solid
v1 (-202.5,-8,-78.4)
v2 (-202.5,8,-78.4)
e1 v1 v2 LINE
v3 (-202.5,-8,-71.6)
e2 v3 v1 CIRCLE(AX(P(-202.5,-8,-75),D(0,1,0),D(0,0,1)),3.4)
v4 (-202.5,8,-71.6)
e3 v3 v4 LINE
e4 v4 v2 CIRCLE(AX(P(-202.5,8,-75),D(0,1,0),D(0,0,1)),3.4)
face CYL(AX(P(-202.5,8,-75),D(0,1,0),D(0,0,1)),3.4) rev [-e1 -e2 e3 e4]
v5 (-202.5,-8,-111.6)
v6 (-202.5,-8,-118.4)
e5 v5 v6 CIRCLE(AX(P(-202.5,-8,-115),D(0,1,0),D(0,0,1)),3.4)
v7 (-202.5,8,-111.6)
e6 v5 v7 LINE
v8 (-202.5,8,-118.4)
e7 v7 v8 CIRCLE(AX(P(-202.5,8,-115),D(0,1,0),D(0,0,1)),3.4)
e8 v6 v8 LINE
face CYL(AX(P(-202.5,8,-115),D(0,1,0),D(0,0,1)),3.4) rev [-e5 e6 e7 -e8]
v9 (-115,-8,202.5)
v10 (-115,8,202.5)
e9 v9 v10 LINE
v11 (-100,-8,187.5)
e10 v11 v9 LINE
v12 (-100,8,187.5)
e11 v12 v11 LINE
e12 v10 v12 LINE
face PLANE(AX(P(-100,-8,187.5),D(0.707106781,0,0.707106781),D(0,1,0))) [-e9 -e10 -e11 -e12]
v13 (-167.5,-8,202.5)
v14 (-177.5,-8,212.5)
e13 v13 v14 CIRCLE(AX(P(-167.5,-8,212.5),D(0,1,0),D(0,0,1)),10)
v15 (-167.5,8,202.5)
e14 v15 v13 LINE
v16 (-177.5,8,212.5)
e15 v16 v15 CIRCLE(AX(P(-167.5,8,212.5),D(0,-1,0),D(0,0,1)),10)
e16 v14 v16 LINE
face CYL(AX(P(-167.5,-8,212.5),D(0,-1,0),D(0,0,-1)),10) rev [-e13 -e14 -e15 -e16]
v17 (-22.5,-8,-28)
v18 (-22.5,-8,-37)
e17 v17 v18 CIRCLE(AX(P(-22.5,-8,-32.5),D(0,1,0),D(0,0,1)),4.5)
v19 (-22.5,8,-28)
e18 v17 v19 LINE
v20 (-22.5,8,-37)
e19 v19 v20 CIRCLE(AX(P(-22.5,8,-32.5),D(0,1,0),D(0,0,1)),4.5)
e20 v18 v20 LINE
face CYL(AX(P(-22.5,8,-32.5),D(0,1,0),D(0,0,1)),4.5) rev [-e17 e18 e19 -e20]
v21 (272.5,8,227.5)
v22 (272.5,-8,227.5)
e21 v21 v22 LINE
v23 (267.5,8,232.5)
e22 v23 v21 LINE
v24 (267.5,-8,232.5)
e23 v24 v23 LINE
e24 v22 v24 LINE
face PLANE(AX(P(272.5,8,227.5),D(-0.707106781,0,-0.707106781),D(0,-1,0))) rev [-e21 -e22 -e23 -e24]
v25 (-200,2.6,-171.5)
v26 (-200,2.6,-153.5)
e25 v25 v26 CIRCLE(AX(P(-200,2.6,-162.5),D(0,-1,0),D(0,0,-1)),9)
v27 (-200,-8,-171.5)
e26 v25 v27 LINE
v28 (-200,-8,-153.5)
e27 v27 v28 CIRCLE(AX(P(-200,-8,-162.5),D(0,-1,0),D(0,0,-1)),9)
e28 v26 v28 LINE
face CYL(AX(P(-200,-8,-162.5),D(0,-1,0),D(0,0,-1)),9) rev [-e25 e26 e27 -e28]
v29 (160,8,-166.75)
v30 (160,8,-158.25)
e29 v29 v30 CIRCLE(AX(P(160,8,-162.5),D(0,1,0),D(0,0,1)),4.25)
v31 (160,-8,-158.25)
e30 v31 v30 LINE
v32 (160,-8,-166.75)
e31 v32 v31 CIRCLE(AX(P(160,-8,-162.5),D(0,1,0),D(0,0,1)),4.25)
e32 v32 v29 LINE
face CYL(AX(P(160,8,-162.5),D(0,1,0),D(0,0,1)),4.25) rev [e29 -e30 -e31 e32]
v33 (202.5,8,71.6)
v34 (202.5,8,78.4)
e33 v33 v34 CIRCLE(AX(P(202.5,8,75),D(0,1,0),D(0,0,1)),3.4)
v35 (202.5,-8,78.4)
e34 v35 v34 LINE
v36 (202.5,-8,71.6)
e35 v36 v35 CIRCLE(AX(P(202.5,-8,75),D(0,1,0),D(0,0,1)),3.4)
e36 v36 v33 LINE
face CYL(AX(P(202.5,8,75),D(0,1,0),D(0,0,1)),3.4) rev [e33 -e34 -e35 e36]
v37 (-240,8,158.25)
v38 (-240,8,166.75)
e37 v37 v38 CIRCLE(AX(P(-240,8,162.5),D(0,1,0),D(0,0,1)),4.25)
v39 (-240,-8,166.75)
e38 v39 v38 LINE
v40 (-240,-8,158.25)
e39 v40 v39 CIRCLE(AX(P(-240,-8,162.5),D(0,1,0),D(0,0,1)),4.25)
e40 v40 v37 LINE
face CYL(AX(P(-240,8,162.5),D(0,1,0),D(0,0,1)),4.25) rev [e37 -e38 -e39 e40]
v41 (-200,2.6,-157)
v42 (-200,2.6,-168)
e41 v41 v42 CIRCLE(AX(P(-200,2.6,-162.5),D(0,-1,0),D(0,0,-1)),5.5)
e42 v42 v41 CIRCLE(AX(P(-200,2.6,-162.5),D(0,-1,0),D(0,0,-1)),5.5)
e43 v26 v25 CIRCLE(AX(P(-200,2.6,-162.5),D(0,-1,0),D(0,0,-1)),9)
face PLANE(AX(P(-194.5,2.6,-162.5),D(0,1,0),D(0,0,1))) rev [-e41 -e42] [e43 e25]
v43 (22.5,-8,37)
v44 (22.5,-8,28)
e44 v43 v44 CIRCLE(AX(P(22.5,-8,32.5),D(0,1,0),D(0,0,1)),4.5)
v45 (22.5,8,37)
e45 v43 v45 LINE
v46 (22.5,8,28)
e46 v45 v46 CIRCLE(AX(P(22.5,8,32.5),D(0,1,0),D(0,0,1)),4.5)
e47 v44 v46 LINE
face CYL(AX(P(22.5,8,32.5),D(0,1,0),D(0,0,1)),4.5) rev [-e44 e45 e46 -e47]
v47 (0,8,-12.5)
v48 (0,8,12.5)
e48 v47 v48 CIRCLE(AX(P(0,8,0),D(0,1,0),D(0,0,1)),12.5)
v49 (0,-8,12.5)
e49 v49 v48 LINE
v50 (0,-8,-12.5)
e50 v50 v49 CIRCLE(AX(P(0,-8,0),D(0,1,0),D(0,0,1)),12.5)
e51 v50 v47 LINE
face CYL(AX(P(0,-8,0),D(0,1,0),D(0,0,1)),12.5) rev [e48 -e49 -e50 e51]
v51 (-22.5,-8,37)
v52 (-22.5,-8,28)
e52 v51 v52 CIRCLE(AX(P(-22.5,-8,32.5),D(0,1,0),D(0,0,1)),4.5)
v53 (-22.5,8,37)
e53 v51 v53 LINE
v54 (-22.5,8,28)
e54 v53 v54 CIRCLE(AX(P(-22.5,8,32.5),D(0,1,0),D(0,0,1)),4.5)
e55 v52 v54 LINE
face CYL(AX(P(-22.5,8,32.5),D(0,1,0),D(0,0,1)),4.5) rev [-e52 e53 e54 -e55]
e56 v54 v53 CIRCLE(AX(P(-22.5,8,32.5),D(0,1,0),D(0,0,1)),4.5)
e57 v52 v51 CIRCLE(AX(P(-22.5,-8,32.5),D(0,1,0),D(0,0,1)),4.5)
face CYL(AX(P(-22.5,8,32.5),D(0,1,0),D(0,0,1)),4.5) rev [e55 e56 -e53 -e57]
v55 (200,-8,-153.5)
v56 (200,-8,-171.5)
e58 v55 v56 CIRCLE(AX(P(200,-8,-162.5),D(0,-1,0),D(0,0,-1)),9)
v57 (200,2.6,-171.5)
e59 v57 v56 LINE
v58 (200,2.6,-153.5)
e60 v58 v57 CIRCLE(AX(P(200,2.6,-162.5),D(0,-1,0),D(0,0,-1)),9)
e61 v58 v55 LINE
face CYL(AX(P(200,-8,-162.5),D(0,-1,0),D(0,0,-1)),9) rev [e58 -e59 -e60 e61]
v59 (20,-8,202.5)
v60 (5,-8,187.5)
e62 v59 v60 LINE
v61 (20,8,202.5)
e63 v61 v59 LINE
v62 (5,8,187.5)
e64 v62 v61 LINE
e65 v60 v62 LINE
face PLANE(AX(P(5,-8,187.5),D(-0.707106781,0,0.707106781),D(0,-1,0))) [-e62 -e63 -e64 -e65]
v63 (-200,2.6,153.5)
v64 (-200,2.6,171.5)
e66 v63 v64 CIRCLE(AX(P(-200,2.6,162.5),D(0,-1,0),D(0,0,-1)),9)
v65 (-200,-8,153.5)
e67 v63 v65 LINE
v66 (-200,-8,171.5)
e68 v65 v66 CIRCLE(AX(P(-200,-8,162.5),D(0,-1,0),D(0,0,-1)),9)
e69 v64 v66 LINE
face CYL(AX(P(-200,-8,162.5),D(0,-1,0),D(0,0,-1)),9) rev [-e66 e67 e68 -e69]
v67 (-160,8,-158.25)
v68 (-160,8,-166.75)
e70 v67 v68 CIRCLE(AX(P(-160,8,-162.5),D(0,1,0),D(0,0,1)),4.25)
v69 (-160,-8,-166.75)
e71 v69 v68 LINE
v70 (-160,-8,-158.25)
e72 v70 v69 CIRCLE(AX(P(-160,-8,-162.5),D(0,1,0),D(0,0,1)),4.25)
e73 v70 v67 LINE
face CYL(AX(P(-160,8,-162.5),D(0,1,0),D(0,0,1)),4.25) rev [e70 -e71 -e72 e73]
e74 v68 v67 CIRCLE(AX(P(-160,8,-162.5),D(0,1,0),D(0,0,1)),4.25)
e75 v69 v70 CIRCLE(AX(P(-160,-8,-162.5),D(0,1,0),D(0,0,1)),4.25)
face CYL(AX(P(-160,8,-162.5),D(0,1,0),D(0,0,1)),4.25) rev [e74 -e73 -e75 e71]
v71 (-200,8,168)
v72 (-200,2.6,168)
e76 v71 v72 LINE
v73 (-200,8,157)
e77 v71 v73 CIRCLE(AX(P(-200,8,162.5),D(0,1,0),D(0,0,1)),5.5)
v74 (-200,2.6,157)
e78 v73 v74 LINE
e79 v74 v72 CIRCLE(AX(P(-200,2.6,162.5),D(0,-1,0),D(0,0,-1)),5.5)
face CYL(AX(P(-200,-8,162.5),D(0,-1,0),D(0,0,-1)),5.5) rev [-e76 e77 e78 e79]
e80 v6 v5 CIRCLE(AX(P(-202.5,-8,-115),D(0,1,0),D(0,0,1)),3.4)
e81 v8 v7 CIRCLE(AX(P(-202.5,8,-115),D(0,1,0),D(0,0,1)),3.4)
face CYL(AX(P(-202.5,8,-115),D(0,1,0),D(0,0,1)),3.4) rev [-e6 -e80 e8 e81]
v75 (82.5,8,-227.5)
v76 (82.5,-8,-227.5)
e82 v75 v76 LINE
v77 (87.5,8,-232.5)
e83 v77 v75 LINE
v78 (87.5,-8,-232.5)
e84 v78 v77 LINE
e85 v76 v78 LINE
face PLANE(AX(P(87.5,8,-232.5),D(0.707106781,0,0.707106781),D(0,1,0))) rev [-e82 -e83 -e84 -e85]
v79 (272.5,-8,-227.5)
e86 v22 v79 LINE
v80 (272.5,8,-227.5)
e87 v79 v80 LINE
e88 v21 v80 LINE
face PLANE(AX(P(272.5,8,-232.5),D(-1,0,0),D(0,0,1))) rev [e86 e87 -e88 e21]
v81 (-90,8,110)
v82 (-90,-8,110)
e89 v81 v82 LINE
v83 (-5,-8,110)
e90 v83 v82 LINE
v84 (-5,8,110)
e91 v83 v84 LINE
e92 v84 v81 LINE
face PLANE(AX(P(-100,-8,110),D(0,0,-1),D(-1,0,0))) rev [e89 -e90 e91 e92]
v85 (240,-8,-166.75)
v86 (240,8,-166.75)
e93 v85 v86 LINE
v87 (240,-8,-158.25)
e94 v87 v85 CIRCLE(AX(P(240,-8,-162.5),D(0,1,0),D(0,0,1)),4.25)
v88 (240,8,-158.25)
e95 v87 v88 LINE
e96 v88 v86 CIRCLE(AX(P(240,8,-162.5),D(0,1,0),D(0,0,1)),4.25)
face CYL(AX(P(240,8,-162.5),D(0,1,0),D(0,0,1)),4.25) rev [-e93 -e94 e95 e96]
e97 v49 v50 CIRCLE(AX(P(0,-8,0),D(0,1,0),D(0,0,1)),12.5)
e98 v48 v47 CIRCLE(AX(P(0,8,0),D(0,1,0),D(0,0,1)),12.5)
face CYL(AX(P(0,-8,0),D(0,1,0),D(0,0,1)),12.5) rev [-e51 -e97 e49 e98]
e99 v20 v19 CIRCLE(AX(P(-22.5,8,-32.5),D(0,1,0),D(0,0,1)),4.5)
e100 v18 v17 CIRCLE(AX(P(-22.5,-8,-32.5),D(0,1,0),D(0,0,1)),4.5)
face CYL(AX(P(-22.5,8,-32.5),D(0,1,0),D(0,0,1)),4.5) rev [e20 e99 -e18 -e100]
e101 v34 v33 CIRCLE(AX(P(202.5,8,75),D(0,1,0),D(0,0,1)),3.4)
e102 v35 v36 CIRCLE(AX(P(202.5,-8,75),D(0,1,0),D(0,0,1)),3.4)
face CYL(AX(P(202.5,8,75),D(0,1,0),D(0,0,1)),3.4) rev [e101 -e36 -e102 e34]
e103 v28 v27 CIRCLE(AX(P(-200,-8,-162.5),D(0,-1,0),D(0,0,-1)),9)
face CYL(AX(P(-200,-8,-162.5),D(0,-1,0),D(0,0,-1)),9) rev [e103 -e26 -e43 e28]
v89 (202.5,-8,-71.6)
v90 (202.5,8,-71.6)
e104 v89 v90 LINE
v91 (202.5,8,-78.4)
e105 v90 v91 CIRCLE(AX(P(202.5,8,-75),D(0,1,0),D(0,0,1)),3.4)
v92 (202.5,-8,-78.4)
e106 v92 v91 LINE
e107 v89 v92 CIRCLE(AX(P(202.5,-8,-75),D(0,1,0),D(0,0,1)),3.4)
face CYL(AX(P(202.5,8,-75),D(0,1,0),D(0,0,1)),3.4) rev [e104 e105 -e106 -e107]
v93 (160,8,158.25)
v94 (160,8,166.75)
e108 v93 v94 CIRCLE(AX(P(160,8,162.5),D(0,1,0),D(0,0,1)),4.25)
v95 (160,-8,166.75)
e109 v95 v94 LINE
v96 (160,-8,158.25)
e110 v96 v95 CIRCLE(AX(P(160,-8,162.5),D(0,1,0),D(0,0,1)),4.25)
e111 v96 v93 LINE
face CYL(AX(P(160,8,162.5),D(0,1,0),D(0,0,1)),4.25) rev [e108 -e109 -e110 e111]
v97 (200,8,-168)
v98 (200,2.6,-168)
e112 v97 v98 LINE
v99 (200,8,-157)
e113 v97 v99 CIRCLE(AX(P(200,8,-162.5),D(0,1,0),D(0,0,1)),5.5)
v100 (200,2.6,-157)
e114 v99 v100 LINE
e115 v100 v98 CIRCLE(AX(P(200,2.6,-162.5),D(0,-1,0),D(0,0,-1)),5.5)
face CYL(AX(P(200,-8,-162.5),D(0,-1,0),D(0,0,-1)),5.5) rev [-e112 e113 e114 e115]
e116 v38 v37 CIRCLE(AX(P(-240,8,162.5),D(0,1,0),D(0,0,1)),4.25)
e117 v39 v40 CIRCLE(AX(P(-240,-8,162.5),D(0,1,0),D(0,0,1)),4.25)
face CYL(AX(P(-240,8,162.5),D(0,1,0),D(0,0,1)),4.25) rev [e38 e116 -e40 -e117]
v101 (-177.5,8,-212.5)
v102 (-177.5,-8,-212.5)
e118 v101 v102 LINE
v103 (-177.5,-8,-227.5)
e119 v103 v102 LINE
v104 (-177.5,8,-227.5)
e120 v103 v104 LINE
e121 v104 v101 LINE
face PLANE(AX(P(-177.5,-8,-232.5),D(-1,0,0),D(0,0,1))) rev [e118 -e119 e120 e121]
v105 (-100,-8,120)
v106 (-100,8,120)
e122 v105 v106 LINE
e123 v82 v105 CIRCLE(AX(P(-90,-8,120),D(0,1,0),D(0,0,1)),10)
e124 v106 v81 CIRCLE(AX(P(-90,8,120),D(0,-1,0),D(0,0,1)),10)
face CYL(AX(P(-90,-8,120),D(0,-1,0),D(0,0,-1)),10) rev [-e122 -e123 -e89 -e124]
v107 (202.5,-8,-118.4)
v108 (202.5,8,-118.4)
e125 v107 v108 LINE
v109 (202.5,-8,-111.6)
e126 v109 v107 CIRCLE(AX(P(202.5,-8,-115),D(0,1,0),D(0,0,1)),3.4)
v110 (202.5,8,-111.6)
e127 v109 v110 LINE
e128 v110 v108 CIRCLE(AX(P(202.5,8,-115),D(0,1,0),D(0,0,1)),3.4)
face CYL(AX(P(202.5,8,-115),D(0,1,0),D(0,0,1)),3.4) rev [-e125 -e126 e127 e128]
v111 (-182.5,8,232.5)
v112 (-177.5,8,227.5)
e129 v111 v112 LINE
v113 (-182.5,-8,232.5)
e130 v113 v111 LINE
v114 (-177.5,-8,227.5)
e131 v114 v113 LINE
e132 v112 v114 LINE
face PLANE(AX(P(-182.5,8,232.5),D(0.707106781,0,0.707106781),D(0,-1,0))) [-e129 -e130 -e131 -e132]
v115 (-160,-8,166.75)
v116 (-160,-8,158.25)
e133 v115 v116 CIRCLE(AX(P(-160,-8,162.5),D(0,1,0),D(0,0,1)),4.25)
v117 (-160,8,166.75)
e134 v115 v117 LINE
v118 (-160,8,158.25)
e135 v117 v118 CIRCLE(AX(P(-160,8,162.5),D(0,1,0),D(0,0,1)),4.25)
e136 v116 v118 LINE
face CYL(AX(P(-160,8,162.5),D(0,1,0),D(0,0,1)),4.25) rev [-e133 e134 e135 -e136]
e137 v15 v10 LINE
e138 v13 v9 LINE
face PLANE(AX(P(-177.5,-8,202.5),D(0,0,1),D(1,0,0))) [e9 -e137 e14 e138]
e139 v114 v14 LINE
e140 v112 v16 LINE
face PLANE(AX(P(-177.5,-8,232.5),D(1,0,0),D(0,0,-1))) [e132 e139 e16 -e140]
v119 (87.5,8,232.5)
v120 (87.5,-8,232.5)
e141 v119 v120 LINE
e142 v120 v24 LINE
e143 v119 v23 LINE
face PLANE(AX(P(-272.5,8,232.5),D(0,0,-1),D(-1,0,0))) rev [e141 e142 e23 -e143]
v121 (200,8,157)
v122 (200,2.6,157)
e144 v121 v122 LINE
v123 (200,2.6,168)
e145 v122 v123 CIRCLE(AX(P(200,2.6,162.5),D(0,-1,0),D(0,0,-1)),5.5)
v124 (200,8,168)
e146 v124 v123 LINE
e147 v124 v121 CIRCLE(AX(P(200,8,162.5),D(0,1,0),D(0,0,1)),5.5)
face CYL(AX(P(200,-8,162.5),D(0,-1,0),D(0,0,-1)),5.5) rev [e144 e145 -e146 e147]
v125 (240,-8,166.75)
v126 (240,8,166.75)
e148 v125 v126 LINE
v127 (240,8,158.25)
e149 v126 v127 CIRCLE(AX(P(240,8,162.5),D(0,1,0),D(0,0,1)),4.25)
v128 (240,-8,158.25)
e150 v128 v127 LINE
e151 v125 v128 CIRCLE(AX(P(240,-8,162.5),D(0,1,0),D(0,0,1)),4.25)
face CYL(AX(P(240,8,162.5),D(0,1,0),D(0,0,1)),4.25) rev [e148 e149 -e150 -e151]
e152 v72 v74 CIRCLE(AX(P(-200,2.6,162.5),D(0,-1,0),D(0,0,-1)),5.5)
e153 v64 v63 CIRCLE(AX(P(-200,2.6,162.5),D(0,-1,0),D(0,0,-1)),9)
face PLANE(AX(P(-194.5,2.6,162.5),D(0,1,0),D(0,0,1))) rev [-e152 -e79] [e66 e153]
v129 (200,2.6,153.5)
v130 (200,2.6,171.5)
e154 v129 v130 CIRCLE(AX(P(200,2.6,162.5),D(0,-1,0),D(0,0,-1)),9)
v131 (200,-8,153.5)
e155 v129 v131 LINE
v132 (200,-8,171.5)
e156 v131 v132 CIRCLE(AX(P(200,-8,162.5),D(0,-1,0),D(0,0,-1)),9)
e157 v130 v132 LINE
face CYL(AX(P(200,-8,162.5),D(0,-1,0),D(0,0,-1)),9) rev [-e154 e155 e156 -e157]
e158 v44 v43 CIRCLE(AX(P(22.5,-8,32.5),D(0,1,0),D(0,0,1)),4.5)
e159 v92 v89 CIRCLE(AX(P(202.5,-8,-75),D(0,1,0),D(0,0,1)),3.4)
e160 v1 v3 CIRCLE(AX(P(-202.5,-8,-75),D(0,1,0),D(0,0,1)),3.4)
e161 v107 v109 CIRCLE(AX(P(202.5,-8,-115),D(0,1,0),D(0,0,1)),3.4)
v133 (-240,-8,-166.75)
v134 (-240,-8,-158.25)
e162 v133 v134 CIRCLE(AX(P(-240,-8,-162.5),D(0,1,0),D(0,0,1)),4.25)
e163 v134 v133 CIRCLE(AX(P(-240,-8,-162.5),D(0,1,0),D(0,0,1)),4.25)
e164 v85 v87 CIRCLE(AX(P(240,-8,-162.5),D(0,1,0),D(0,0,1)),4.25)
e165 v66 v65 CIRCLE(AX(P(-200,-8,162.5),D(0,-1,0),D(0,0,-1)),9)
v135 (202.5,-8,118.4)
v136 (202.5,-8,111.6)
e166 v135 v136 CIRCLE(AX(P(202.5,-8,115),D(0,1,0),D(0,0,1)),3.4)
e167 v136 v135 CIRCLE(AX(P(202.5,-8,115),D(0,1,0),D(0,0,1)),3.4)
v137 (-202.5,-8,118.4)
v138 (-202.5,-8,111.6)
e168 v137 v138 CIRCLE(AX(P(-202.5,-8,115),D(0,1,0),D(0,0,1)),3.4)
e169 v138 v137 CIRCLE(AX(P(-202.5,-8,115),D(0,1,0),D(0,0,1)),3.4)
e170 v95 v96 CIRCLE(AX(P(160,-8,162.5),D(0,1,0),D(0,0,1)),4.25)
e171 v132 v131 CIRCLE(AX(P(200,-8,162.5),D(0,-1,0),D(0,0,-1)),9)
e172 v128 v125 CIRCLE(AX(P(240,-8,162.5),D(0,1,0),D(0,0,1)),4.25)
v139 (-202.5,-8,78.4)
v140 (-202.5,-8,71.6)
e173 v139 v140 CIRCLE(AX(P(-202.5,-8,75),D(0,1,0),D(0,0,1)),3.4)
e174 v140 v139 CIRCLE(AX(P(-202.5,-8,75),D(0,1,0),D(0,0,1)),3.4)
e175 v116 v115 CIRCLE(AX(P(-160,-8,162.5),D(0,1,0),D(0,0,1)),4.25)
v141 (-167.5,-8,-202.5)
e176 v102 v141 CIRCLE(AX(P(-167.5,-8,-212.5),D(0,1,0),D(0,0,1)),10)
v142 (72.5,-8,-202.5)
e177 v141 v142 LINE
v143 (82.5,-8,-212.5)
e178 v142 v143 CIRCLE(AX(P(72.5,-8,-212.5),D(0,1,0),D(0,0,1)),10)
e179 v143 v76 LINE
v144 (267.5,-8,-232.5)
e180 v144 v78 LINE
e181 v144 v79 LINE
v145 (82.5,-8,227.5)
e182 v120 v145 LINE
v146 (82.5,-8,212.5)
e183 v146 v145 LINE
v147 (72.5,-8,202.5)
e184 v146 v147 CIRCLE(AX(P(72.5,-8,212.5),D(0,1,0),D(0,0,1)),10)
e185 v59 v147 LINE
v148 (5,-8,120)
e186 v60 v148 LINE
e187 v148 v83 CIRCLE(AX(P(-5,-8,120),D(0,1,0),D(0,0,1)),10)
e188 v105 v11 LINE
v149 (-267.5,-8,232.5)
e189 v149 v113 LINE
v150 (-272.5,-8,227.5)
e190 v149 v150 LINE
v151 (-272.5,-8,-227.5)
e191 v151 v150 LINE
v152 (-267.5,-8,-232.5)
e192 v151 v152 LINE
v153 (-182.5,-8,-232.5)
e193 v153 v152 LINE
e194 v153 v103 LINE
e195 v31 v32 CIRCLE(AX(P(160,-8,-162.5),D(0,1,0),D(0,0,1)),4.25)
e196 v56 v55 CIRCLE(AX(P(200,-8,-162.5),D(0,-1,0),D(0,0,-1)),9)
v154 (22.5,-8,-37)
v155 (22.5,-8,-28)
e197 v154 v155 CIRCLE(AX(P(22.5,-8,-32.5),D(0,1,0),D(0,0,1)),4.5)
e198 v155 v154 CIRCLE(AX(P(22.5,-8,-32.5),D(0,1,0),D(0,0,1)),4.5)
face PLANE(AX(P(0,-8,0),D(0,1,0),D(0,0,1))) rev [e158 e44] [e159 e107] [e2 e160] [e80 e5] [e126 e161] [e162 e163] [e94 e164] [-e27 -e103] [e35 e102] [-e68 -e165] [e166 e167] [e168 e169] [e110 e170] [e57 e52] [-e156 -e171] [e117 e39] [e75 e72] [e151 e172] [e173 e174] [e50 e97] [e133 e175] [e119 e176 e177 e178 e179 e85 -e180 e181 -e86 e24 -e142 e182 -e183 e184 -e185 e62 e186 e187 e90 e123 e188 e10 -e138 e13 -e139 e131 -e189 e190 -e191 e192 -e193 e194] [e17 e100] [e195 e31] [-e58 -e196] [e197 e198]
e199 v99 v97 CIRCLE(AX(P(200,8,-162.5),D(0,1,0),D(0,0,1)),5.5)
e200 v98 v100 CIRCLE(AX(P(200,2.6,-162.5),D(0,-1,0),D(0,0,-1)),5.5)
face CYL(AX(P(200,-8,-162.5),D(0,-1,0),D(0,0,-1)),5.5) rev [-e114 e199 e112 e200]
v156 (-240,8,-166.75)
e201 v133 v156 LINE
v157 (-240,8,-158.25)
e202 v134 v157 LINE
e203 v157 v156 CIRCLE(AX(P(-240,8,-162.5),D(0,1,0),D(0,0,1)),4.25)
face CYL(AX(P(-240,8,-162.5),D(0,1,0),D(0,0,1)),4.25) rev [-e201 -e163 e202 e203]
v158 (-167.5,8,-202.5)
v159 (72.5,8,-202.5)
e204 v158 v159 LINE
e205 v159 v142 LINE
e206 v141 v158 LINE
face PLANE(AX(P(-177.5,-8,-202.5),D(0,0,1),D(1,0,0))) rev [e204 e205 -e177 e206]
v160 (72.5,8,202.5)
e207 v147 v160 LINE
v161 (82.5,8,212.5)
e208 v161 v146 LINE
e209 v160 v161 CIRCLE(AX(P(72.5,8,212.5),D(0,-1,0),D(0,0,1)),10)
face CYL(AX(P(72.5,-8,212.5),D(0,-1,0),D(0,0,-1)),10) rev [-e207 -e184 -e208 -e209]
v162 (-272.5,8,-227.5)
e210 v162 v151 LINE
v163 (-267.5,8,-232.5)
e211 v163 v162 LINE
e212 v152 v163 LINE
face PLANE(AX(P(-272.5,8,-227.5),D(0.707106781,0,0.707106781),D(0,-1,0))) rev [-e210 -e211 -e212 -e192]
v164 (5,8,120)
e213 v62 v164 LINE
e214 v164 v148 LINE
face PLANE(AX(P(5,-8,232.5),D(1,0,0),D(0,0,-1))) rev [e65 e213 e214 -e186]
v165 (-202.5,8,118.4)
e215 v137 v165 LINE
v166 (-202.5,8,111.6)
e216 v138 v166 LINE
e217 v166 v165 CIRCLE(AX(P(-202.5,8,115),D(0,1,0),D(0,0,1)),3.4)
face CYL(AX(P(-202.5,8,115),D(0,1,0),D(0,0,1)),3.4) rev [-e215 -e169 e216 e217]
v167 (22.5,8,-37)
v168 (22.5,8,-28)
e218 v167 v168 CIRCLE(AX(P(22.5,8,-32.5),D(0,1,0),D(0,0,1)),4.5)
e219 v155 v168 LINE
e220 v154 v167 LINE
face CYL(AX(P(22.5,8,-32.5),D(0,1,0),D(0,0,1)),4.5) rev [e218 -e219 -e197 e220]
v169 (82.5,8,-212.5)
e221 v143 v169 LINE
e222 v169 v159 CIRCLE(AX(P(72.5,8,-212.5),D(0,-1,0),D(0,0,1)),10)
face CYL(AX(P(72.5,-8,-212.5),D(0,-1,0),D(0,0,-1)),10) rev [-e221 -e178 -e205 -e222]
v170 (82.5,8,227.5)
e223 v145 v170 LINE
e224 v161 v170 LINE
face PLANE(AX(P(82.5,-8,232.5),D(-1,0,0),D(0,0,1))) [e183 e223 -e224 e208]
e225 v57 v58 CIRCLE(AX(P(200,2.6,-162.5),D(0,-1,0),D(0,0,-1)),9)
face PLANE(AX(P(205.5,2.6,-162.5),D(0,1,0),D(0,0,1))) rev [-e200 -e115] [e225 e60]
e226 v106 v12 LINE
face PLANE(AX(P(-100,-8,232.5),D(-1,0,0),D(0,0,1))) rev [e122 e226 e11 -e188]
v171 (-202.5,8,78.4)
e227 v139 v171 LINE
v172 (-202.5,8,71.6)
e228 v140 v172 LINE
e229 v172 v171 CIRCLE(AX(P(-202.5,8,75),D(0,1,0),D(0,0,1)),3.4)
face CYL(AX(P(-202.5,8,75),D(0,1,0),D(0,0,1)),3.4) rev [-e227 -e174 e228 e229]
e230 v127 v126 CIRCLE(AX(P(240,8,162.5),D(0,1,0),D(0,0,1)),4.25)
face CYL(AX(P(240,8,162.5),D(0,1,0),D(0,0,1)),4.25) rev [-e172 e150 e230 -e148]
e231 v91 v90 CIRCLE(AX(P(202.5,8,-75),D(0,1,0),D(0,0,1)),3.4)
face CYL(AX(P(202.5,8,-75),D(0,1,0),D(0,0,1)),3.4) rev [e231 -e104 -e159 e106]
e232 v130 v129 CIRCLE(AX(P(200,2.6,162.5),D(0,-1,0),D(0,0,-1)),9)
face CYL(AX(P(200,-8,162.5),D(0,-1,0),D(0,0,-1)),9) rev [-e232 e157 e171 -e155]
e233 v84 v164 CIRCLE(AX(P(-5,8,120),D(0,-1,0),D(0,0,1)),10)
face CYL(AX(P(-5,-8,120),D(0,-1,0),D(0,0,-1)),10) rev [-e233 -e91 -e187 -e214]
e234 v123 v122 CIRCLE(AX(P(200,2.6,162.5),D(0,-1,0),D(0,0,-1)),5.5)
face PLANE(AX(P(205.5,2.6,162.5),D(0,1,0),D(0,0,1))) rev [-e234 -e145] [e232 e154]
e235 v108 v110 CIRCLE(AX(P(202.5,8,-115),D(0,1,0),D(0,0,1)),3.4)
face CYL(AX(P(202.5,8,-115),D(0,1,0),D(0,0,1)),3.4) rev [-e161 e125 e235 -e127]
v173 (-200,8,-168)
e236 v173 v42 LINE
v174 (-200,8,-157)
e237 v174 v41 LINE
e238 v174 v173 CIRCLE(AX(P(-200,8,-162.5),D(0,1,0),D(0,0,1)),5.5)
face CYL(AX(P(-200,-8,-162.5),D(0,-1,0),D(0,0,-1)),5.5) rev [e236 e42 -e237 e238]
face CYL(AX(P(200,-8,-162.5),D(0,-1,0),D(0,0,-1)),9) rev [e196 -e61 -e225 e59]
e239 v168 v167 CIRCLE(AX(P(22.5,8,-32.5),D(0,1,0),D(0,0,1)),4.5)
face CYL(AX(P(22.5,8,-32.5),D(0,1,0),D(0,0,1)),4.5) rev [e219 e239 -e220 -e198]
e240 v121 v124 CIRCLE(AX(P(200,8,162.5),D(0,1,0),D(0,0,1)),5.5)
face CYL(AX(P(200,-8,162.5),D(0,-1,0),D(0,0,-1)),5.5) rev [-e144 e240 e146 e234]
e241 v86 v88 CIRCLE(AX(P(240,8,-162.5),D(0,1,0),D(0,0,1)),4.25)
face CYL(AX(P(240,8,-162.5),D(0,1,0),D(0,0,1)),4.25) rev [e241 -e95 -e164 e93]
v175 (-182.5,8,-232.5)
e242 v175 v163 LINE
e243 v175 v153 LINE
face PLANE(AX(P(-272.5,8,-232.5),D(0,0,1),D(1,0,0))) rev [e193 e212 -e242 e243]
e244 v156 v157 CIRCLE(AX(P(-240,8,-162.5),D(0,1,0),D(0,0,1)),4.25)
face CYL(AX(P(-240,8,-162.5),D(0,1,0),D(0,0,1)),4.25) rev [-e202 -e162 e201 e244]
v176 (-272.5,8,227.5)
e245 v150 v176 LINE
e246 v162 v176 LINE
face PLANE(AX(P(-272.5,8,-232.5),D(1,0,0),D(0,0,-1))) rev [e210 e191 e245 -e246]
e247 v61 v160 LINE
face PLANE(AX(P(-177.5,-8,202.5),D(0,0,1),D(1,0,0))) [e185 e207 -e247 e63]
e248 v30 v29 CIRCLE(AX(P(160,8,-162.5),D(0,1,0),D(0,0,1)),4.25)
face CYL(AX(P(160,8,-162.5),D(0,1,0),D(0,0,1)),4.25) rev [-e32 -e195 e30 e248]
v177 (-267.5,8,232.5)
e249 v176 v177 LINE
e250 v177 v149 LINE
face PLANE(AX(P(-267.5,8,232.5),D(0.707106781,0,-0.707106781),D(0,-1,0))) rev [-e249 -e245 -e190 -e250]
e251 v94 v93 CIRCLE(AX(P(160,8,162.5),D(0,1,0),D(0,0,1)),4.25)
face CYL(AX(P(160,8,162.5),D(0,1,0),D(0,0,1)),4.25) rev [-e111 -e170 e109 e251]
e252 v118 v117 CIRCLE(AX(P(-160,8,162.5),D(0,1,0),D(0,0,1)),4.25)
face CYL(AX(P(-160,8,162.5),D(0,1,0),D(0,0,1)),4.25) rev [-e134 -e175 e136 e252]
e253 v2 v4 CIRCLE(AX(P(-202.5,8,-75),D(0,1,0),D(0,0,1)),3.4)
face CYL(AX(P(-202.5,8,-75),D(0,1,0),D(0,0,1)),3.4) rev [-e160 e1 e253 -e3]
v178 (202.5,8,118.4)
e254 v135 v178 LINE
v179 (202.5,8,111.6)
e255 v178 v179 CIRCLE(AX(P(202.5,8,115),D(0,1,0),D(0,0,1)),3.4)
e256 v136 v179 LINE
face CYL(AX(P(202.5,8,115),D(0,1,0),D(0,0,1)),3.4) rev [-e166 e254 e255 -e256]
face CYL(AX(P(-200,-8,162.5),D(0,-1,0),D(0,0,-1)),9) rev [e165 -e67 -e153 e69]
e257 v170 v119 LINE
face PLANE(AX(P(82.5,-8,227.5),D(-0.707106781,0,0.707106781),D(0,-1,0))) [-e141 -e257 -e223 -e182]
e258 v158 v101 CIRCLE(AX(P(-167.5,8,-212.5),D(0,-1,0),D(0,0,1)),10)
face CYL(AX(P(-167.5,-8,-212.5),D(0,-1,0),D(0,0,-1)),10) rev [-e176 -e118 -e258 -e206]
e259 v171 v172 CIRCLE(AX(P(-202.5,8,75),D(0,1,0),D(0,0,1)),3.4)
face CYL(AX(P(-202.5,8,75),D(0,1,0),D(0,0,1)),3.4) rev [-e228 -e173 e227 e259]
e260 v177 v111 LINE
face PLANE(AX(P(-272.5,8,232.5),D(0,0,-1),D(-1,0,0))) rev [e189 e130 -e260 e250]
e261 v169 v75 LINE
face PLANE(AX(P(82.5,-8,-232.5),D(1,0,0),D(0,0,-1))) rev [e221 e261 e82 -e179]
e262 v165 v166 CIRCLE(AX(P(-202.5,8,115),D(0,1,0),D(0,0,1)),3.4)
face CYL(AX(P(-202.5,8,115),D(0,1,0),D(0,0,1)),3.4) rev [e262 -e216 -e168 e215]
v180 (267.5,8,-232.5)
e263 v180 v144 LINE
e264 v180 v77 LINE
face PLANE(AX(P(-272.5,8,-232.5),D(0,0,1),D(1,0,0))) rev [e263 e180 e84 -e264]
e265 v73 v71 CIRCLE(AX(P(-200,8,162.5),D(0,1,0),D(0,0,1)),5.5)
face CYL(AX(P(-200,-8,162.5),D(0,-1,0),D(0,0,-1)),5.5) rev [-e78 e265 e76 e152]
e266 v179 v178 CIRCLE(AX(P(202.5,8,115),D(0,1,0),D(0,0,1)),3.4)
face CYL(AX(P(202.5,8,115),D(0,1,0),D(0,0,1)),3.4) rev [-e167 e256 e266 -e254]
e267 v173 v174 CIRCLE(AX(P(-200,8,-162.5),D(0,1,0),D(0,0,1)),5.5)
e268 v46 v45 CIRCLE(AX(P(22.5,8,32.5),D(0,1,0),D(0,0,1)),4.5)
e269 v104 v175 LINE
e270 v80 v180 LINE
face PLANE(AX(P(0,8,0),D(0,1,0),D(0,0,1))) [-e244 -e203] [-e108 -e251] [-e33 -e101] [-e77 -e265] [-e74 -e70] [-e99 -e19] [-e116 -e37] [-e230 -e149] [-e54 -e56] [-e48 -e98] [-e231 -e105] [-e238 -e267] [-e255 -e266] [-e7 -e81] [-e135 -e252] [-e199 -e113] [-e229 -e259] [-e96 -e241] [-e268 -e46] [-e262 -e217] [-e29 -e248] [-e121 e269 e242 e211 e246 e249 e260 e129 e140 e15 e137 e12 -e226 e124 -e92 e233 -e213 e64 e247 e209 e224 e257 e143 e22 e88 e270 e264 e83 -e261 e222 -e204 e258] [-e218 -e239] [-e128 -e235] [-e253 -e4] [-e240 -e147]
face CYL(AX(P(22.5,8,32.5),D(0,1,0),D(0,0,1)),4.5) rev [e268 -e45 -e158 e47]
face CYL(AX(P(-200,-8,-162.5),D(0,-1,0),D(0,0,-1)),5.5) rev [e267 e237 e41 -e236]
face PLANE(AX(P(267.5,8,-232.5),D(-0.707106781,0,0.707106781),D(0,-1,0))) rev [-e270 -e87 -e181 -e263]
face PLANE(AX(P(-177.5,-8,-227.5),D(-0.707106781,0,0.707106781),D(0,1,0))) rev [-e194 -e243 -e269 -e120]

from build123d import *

# Parameters (mm, degrees)
SKETCH_1_W                     = 545
SKETCH_1_H                     = 465
EXTRUDE_1_DEPTH                = 8
SKETCH_2_W                     = 260
SKETCH_2_H                     = 30
CUT_EXTRUDE_1_DEPTH            = 16
SKETCH_3_W                     = 105
SKETCH_3_H                     = 122.5
CUT_EXTRUDE_2_DEPTH            = 359.564499079
HOLE_WIZARD_M8_2_D             = 6.8
MIRROR_3_COPY_1_D              = 6.8
CHAMFER_1_SIZE                 = 15
FILLET_1_R                     = 10
HOLE_WIZARD_9_0_9_1_D          = 9
HOLE_WIZARD_M10_1_D            = 11
HOLE_WIZARD_M10_1_DEPTH        = 24.5
HOLE_WIZARD_M10_1_CBORE_D      = 18
HOLE_WIZARD_M10_1_CBORE_DEPTH  = 10.6
HOLE_WIZARD_M10_1_TIP          = 3.304733405
CHAMFER_2_SIZE                 = 5
HOLE_WIZARD_M10_1_2_AT_2_COUNT = 2
HOLE_WIZARD_M10_1_2_AT_2_PITCH = 80
SKETCH_17_R                    = 12.5
CUT_EXTRUDE_10_DEPTH           = 359.564499079


with BuildPart() as part:
    # 草图1 → 凸台-拉伸1 (new, symmetric)
    with BuildSketch(Plane(origin=(0, 0, 0), x_dir=(1, 0, 0), z_dir=(0, 1, 0))):
        Rectangle(SKETCH_1_W, SKETCH_1_H)
    extrude(amount=EXTRUDE_1_DEPTH, both=True)

    # 草图2 → 切除-拉伸1 (cut)
    with BuildSketch(Plane(origin=(0, 8, 0), x_dir=(1, 0, 0), z_dir=(0, 1, 0))):
        with Locations((-47.5, 217.5)):
            Rectangle(SKETCH_2_W, SKETCH_2_H)
    cut_extrude_1 = extrude(amount=-CUT_EXTRUDE_1_DEPTH, mode=Mode.SUBTRACT)

    # 镜向1: 切除-拉伸1 across plane
    add(cut_extrude_1.mirror(Plane.XY), mode=Mode.SUBTRACT)

    # 草图3 → 切除-拉伸2 (cut, through all)
    with BuildSketch(Plane(origin=(0, 8, 0), x_dir=(1, 0, 0), z_dir=(0, 1, 0))):
        with Locations((-47.5, -171.25)):
            Rectangle(SKETCH_3_W, SKETCH_3_H)
    extrude(amount=-CUT_EXTRUDE_2_DEPTH, mode=Mode.SUBTRACT)

    # M8 螺纹孔2 (through all)
    with Locations(Plane(origin=(0, 8, 0), x_dir=(1, 0, 0), z_dir=(0, 1, 0))):
        with Locations((202.5, -115), (202.5, -75)):
            hole_wizard_m8_2 = Hole(HOLE_WIZARD_M8_2_D / 2)

    # 镜向2: M8 螺纹孔2 across plane
    add(hole_wizard_m8_2.mirror(Plane(origin=(0, 0, 0), x_dir=(0, 0, 1), z_dir=(1, 0, 0))), mode=Mode.SUBTRACT)

    # 镜向3: M8 螺纹孔2 across plane
    add(hole_wizard_m8_2.mirror(Plane.XY), mode=Mode.SUBTRACT)

    # 镜向3 copy 1 (through all)
    with Locations(Plane(origin=(0, 8, 0), x_dir=(-1, 0, 0), z_dir=(0, 1, 0))):
        with Locations((202.5, -115), (202.5, -75)):
            Hole(MIRROR_3_COPY_1_D / 2)

    # 倒角1
    chamfer_1_edges = [part.edges().sort_by_distance(p)[0] for p in [
        (5, 0, 202.5),
        (-100, 0, 202.5),
    ]]
    chamfer(chamfer_1_edges, length=CHAMFER_1_SIZE)

    # 圆角1
    fillet_1_edges = [part.edges().sort_by_distance(p)[0] for p in [
        (-177.5, 0, -202.5),
        (82.5, 0, -202.5),
        (-177.5, 0, 202.5),
        (82.5, 0, 202.5),
        (-100, 0, 110),
        (5, 0, 110),
    ]]
    fillet(fillet_1_edges, radius=FILLET_1_R)

    # Ø9.0 (9) 直径孔1 (through all)
    with Locations(Plane(origin=(0, 8, 0), x_dir=(1, 0, 0), z_dir=(0, 1, 0))):
        with Locations((22.5, -32.5), (-22.5, -32.5), (-22.5, 32.5), (22.5, 32.5)):
            Hole(HOLE_WIZARD_9_0_9_1_D / 2)

    # Hole Wizard M10 _1
    with Locations(Plane.XZ.offset(8)):
        with Locations((-200, -162.5), (200, -162.5), (-200, 162.5), (200, 162.5)):
            CounterBoreHole(HOLE_WIZARD_M10_1_D / 2, HOLE_WIZARD_M10_1_CBORE_D / 2, HOLE_WIZARD_M10_1_CBORE_DEPTH, depth=HOLE_WIZARD_M10_1_DEPTH)
            with Locations((0, 0, -(HOLE_WIZARD_M10_1_DEPTH + HOLE_WIZARD_M10_1_TIP / 2))):  # 118° drill point
                Cone(0, HOLE_WIZARD_M10_1_D / 2, HOLE_WIZARD_M10_1_TIP, mode=Mode.SUBTRACT)

    # 倒角2
    chamfer_2_edges = [part.edges().sort_by_distance(p)[0] for p in [
        (-177.5, 0, -232.5),
        (82.5, 0, -232.5),
        (-177.5, 0, 232.5),
        (82.5, 0, 232.5),
        (272.5, 0, 232.5),
        (-272.5, 0, 232.5),
        (-272.5, 0, -232.5),
        (272.5, 0, -232.5),
    ]]
    chamfer(chamfer_2_edges, length=CHAMFER_2_SIZE)

    # 草图15 → Hole Wizard M10 _1 2 (revolve, cut)
    with BuildSketch(Plane(origin=(-240, 8, 162.5), x_dir=(0, 0, 1), z_dir=(1, 0, 0))):
        Polygon((0, 0), (0, 27.053657631), (4.25, 24.5), (4.25, 0), align=None)
    hole_wizard_m10_1_2 = revolve(axis=Axis((-240, 14.35, 162.5), (0, -1, 0)), mode=Mode.SUBTRACT)

    # Hole Wizard M10 _1 2 at 2: Hole Wizard M10 _1 2 ×2
    with Locations(*[(i * HOLE_WIZARD_M10_1_2_AT_2_PITCH, 0, 0) for i in range(1, HOLE_WIZARD_M10_1_2_AT_2_COUNT)]):
        add(hole_wizard_m10_1_2, mode=Mode.SUBTRACT)

    # 镜向4: Hole Wizard M10 _1 2 across plane
    add(hole_wizard_m10_1_2.mirror(Plane.XY), mode=Mode.SUBTRACT)

    # 镜向4 copy 1 sketch → 镜向4 copy 1 (revolve, cut)
    with BuildSketch(Plane(origin=(-160, 8, -162.5), x_dir=(0, 0, -1), z_dir=(1, 0, 0))):
        Polygon((0, 0), (0, -27.053657631), (4.25, -24.5), (4.25, 0), align=None)
    revolve(axis=Axis((-160, 14.35, -162.5), (0, 1, 0)), mode=Mode.SUBTRACT)

    # 镜向5: Hole Wizard M10 _1 2 across plane
    add(hole_wizard_m10_1_2.mirror(Plane(origin=(0, 0, 0), x_dir=(0, 0, 1), z_dir=(1, 0, 0))), mode=Mode.SUBTRACT)

    # 镜向5 copy 1 sketch → 镜向5 copy 1 (revolve, cut)
    with BuildSketch(Plane(origin=(160, 8, 162.5), x_dir=(0, 0, 1), z_dir=(-1, 0, 0))):
        Polygon((0, 0), (0, -27.053657631), (4.25, -24.5), (4.25, 0), align=None)
    revolve(axis=Axis((160, 14.35, 162.5), (0, 1, 0)), mode=Mode.SUBTRACT)

    # 镜向5 copy 2 sketch → 镜向5 copy 2 (revolve, cut)
    with BuildSketch(Plane(origin=(240, 8, -162.5), x_dir=(0, 0, -1), z_dir=(-1, 0, 0))):
        Polygon((0, 0), (0, 27.053657631), (4.25, 24.5), (4.25, 0), align=None)
    revolve(axis=Axis((240, 14.35, -162.5), (0, -1, 0)), mode=Mode.SUBTRACT)

    # 镜向5 copy 3 sketch → 镜向5 copy 3 (revolve, cut)
    with BuildSketch(Plane(origin=(160, 8, -162.5), x_dir=(0, 0, -1), z_dir=(-1, 0, 0))):
        Polygon((0, 0), (0, 27.053657631), (4.25, 24.5), (4.25, 0), align=None)
    revolve(axis=Axis((160, 14.35, -162.5), (0, -1, 0)), mode=Mode.SUBTRACT)

    # 草图17 → 切除-拉伸10 (cut, through all)
    with BuildSketch(Plane(origin=(0, 8, 0), x_dir=(1, 0, 0), z_dir=(0, 1, 0))):
        with Locations(Location((0, 0, 0), (0, 0, 270))):
            Circle(SKETCH_17_R)
    extrude(amount=-CUT_EXTRUDE_10_DEPTH, mode=Mode.SUBTRACT)


solid = part.part
